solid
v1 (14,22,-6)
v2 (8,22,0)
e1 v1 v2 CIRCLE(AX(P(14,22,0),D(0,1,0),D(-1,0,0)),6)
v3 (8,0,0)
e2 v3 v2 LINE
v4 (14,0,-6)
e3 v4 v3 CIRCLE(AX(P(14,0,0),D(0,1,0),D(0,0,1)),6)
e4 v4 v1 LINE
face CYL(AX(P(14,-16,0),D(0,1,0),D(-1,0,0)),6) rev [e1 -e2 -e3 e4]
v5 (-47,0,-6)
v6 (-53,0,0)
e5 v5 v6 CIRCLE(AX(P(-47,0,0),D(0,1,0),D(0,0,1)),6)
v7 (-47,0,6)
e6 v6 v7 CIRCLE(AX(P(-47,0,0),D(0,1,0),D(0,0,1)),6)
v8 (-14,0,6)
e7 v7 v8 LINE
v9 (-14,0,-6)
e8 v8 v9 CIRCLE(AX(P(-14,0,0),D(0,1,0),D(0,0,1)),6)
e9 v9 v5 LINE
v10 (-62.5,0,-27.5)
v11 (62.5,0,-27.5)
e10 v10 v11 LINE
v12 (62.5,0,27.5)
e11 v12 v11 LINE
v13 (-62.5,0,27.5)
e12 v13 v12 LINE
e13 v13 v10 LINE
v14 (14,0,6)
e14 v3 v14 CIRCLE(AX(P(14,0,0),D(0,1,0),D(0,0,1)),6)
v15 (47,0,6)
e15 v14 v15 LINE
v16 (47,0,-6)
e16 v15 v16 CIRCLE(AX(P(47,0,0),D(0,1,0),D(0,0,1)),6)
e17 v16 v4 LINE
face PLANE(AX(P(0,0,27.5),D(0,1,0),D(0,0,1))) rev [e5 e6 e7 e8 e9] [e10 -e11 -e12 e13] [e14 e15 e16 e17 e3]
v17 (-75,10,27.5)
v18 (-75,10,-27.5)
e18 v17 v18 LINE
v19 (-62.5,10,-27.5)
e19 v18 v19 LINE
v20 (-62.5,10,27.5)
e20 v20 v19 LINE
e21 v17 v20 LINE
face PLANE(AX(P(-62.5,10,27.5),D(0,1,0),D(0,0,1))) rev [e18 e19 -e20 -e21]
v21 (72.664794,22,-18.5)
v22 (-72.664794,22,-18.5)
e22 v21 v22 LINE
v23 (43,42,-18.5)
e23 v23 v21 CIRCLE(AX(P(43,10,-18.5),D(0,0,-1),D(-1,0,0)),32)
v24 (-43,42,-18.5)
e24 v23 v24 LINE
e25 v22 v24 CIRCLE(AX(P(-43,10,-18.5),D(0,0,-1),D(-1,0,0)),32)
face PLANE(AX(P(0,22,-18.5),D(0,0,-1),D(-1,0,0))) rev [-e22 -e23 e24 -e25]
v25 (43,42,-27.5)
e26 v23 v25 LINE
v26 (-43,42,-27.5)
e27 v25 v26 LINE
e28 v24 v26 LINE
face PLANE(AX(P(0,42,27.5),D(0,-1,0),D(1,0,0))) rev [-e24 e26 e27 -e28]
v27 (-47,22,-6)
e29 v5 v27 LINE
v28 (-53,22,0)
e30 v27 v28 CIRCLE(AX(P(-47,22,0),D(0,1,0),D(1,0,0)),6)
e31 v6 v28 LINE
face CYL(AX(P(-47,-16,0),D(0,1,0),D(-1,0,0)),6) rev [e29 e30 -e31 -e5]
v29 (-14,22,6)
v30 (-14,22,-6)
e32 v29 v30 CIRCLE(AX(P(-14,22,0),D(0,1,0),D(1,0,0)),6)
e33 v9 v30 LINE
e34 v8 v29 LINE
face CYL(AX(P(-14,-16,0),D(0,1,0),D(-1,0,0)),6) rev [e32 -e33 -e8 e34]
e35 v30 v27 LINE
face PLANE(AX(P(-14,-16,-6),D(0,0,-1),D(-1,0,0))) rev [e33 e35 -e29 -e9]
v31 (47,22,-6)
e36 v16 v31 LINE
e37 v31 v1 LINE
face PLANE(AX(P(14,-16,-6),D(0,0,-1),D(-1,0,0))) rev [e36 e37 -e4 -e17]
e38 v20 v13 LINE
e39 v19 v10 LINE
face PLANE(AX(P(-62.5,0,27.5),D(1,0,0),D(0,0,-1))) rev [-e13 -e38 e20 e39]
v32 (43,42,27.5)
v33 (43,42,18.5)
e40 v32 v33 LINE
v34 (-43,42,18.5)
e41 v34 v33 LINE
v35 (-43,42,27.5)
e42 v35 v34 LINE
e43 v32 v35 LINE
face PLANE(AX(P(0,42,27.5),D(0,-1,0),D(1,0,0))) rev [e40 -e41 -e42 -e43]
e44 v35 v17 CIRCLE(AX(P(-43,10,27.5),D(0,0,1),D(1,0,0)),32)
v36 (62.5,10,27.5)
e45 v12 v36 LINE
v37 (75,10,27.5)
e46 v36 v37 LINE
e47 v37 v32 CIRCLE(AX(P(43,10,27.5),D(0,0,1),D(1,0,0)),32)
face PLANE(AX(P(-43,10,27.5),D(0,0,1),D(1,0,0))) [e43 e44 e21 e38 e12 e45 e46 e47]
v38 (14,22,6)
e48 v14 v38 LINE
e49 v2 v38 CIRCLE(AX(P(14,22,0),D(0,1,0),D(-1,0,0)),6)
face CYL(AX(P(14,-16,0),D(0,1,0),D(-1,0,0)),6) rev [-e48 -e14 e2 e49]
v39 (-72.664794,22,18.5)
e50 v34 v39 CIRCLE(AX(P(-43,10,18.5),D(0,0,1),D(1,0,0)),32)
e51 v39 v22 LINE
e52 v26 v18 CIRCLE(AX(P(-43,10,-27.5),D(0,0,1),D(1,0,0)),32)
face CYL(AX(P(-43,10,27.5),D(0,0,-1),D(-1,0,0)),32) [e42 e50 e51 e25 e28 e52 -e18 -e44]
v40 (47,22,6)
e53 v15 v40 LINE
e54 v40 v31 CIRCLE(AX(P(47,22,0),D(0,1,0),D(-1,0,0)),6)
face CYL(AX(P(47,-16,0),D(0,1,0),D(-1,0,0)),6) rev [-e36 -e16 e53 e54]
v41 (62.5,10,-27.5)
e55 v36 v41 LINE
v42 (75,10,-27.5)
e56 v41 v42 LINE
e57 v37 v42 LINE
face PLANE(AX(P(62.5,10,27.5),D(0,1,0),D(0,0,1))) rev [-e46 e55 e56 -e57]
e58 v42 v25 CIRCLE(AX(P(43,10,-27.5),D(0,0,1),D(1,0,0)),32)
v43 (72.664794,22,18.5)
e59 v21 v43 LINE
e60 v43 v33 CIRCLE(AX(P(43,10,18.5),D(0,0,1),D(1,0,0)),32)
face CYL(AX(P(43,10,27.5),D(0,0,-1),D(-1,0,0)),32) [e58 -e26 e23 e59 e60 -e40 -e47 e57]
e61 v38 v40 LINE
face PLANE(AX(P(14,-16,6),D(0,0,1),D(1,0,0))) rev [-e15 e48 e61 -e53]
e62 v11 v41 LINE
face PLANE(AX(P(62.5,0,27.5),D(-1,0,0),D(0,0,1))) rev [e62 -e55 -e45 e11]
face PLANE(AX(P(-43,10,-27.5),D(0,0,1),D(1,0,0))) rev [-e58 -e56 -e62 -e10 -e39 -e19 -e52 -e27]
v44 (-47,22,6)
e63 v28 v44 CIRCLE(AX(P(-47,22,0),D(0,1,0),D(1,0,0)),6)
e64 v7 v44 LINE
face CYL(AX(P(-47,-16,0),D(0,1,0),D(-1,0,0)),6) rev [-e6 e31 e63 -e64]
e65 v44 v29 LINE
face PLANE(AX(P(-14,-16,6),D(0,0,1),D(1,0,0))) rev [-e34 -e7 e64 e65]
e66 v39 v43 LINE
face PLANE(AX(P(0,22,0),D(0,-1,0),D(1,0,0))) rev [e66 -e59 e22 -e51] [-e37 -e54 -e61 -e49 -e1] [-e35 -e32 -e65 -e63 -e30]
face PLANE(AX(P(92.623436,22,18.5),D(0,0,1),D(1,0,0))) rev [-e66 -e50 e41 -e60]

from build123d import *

# Parameters (mm, degrees)
SLIDE_BLOCK_BODY_DEPTH       = 27.5
CENTRE_CHANNEL_37_WIDE_DEPTH = 20
TWIN_SLOTS_2XR6_DEPTH        = 38


with BuildPart() as part:
    # Block Profile Sketch → Slide Block Body (new, symmetric)
    with BuildSketch(Plane.XY):
        with BuildLine():
            Line((0, 0), (62.5, 0))
            Line((62.5, 0), (62.5, 10))
            Line((62.5, 10), (75, 10))
            ThreePointArc((75, 10), (65.627416998, 32.627416998), (43, 42))
            Line((43, 42), (0, 42))
            Line((0, 42), (-43, 42))
            ThreePointArc((-43, 42), (-65.627416998, 32.627416998), (-75, 10))
            Line((-75, 10), (-62.5, 10))
            Line((-62.5, 10), (-62.5, 0))
            Line((-62.5, 0), (0, 0))
        make_face()
    extrude(amount=SLIDE_BLOCK_BODY_DEPTH, both=True)

    # Centre Channel Sketch → Centre Channel 37 Wide (cut)
    with BuildSketch(Plane(origin=(0, 42, 0), x_dir=(1, 0, 0), z_dir=(0, 1, 0))):
        Polygon((0, 18.5), (92.62343554, 18.5), (92.62343554, -18.5), (-101.990097212, -18.5), (-101.990097212, 18.5), align=None)
    extrude(amount=-CENTRE_CHANNEL_37_WIDE_DEPTH, mode=Mode.SUBTRACT)

    # Twin Slots Sketch → Twin Slots 2xR6 (cut)
    with BuildSketch(Plane(origin=(0, 22, 0), x_dir=(1, 0, 0), z_dir=(0, 1, 0))):
        with BuildLine():
            Line((-14, -6), (-47, -6))
            ThreePointArc((-47, -6), (-53, 0), (-47, 6))
            Line((-47, 6), (-14, 6))
            ThreePointArc((-14, 6), (-8, 0), (-14, -6))
        make_face()
        with BuildLine():
            Line((14, 6), (47, 6))
            ThreePointArc((47, 6), (53, 0), (47, -6))
            Line((47, -6), (14, -6))
            ThreePointArc((14, -6), (8, 0), (14, 6))
        make_face()
    extrude(amount=-TWIN_SLOTS_2XR6_DEPTH, mode=Mode.SUBTRACT)


solid = part.part
